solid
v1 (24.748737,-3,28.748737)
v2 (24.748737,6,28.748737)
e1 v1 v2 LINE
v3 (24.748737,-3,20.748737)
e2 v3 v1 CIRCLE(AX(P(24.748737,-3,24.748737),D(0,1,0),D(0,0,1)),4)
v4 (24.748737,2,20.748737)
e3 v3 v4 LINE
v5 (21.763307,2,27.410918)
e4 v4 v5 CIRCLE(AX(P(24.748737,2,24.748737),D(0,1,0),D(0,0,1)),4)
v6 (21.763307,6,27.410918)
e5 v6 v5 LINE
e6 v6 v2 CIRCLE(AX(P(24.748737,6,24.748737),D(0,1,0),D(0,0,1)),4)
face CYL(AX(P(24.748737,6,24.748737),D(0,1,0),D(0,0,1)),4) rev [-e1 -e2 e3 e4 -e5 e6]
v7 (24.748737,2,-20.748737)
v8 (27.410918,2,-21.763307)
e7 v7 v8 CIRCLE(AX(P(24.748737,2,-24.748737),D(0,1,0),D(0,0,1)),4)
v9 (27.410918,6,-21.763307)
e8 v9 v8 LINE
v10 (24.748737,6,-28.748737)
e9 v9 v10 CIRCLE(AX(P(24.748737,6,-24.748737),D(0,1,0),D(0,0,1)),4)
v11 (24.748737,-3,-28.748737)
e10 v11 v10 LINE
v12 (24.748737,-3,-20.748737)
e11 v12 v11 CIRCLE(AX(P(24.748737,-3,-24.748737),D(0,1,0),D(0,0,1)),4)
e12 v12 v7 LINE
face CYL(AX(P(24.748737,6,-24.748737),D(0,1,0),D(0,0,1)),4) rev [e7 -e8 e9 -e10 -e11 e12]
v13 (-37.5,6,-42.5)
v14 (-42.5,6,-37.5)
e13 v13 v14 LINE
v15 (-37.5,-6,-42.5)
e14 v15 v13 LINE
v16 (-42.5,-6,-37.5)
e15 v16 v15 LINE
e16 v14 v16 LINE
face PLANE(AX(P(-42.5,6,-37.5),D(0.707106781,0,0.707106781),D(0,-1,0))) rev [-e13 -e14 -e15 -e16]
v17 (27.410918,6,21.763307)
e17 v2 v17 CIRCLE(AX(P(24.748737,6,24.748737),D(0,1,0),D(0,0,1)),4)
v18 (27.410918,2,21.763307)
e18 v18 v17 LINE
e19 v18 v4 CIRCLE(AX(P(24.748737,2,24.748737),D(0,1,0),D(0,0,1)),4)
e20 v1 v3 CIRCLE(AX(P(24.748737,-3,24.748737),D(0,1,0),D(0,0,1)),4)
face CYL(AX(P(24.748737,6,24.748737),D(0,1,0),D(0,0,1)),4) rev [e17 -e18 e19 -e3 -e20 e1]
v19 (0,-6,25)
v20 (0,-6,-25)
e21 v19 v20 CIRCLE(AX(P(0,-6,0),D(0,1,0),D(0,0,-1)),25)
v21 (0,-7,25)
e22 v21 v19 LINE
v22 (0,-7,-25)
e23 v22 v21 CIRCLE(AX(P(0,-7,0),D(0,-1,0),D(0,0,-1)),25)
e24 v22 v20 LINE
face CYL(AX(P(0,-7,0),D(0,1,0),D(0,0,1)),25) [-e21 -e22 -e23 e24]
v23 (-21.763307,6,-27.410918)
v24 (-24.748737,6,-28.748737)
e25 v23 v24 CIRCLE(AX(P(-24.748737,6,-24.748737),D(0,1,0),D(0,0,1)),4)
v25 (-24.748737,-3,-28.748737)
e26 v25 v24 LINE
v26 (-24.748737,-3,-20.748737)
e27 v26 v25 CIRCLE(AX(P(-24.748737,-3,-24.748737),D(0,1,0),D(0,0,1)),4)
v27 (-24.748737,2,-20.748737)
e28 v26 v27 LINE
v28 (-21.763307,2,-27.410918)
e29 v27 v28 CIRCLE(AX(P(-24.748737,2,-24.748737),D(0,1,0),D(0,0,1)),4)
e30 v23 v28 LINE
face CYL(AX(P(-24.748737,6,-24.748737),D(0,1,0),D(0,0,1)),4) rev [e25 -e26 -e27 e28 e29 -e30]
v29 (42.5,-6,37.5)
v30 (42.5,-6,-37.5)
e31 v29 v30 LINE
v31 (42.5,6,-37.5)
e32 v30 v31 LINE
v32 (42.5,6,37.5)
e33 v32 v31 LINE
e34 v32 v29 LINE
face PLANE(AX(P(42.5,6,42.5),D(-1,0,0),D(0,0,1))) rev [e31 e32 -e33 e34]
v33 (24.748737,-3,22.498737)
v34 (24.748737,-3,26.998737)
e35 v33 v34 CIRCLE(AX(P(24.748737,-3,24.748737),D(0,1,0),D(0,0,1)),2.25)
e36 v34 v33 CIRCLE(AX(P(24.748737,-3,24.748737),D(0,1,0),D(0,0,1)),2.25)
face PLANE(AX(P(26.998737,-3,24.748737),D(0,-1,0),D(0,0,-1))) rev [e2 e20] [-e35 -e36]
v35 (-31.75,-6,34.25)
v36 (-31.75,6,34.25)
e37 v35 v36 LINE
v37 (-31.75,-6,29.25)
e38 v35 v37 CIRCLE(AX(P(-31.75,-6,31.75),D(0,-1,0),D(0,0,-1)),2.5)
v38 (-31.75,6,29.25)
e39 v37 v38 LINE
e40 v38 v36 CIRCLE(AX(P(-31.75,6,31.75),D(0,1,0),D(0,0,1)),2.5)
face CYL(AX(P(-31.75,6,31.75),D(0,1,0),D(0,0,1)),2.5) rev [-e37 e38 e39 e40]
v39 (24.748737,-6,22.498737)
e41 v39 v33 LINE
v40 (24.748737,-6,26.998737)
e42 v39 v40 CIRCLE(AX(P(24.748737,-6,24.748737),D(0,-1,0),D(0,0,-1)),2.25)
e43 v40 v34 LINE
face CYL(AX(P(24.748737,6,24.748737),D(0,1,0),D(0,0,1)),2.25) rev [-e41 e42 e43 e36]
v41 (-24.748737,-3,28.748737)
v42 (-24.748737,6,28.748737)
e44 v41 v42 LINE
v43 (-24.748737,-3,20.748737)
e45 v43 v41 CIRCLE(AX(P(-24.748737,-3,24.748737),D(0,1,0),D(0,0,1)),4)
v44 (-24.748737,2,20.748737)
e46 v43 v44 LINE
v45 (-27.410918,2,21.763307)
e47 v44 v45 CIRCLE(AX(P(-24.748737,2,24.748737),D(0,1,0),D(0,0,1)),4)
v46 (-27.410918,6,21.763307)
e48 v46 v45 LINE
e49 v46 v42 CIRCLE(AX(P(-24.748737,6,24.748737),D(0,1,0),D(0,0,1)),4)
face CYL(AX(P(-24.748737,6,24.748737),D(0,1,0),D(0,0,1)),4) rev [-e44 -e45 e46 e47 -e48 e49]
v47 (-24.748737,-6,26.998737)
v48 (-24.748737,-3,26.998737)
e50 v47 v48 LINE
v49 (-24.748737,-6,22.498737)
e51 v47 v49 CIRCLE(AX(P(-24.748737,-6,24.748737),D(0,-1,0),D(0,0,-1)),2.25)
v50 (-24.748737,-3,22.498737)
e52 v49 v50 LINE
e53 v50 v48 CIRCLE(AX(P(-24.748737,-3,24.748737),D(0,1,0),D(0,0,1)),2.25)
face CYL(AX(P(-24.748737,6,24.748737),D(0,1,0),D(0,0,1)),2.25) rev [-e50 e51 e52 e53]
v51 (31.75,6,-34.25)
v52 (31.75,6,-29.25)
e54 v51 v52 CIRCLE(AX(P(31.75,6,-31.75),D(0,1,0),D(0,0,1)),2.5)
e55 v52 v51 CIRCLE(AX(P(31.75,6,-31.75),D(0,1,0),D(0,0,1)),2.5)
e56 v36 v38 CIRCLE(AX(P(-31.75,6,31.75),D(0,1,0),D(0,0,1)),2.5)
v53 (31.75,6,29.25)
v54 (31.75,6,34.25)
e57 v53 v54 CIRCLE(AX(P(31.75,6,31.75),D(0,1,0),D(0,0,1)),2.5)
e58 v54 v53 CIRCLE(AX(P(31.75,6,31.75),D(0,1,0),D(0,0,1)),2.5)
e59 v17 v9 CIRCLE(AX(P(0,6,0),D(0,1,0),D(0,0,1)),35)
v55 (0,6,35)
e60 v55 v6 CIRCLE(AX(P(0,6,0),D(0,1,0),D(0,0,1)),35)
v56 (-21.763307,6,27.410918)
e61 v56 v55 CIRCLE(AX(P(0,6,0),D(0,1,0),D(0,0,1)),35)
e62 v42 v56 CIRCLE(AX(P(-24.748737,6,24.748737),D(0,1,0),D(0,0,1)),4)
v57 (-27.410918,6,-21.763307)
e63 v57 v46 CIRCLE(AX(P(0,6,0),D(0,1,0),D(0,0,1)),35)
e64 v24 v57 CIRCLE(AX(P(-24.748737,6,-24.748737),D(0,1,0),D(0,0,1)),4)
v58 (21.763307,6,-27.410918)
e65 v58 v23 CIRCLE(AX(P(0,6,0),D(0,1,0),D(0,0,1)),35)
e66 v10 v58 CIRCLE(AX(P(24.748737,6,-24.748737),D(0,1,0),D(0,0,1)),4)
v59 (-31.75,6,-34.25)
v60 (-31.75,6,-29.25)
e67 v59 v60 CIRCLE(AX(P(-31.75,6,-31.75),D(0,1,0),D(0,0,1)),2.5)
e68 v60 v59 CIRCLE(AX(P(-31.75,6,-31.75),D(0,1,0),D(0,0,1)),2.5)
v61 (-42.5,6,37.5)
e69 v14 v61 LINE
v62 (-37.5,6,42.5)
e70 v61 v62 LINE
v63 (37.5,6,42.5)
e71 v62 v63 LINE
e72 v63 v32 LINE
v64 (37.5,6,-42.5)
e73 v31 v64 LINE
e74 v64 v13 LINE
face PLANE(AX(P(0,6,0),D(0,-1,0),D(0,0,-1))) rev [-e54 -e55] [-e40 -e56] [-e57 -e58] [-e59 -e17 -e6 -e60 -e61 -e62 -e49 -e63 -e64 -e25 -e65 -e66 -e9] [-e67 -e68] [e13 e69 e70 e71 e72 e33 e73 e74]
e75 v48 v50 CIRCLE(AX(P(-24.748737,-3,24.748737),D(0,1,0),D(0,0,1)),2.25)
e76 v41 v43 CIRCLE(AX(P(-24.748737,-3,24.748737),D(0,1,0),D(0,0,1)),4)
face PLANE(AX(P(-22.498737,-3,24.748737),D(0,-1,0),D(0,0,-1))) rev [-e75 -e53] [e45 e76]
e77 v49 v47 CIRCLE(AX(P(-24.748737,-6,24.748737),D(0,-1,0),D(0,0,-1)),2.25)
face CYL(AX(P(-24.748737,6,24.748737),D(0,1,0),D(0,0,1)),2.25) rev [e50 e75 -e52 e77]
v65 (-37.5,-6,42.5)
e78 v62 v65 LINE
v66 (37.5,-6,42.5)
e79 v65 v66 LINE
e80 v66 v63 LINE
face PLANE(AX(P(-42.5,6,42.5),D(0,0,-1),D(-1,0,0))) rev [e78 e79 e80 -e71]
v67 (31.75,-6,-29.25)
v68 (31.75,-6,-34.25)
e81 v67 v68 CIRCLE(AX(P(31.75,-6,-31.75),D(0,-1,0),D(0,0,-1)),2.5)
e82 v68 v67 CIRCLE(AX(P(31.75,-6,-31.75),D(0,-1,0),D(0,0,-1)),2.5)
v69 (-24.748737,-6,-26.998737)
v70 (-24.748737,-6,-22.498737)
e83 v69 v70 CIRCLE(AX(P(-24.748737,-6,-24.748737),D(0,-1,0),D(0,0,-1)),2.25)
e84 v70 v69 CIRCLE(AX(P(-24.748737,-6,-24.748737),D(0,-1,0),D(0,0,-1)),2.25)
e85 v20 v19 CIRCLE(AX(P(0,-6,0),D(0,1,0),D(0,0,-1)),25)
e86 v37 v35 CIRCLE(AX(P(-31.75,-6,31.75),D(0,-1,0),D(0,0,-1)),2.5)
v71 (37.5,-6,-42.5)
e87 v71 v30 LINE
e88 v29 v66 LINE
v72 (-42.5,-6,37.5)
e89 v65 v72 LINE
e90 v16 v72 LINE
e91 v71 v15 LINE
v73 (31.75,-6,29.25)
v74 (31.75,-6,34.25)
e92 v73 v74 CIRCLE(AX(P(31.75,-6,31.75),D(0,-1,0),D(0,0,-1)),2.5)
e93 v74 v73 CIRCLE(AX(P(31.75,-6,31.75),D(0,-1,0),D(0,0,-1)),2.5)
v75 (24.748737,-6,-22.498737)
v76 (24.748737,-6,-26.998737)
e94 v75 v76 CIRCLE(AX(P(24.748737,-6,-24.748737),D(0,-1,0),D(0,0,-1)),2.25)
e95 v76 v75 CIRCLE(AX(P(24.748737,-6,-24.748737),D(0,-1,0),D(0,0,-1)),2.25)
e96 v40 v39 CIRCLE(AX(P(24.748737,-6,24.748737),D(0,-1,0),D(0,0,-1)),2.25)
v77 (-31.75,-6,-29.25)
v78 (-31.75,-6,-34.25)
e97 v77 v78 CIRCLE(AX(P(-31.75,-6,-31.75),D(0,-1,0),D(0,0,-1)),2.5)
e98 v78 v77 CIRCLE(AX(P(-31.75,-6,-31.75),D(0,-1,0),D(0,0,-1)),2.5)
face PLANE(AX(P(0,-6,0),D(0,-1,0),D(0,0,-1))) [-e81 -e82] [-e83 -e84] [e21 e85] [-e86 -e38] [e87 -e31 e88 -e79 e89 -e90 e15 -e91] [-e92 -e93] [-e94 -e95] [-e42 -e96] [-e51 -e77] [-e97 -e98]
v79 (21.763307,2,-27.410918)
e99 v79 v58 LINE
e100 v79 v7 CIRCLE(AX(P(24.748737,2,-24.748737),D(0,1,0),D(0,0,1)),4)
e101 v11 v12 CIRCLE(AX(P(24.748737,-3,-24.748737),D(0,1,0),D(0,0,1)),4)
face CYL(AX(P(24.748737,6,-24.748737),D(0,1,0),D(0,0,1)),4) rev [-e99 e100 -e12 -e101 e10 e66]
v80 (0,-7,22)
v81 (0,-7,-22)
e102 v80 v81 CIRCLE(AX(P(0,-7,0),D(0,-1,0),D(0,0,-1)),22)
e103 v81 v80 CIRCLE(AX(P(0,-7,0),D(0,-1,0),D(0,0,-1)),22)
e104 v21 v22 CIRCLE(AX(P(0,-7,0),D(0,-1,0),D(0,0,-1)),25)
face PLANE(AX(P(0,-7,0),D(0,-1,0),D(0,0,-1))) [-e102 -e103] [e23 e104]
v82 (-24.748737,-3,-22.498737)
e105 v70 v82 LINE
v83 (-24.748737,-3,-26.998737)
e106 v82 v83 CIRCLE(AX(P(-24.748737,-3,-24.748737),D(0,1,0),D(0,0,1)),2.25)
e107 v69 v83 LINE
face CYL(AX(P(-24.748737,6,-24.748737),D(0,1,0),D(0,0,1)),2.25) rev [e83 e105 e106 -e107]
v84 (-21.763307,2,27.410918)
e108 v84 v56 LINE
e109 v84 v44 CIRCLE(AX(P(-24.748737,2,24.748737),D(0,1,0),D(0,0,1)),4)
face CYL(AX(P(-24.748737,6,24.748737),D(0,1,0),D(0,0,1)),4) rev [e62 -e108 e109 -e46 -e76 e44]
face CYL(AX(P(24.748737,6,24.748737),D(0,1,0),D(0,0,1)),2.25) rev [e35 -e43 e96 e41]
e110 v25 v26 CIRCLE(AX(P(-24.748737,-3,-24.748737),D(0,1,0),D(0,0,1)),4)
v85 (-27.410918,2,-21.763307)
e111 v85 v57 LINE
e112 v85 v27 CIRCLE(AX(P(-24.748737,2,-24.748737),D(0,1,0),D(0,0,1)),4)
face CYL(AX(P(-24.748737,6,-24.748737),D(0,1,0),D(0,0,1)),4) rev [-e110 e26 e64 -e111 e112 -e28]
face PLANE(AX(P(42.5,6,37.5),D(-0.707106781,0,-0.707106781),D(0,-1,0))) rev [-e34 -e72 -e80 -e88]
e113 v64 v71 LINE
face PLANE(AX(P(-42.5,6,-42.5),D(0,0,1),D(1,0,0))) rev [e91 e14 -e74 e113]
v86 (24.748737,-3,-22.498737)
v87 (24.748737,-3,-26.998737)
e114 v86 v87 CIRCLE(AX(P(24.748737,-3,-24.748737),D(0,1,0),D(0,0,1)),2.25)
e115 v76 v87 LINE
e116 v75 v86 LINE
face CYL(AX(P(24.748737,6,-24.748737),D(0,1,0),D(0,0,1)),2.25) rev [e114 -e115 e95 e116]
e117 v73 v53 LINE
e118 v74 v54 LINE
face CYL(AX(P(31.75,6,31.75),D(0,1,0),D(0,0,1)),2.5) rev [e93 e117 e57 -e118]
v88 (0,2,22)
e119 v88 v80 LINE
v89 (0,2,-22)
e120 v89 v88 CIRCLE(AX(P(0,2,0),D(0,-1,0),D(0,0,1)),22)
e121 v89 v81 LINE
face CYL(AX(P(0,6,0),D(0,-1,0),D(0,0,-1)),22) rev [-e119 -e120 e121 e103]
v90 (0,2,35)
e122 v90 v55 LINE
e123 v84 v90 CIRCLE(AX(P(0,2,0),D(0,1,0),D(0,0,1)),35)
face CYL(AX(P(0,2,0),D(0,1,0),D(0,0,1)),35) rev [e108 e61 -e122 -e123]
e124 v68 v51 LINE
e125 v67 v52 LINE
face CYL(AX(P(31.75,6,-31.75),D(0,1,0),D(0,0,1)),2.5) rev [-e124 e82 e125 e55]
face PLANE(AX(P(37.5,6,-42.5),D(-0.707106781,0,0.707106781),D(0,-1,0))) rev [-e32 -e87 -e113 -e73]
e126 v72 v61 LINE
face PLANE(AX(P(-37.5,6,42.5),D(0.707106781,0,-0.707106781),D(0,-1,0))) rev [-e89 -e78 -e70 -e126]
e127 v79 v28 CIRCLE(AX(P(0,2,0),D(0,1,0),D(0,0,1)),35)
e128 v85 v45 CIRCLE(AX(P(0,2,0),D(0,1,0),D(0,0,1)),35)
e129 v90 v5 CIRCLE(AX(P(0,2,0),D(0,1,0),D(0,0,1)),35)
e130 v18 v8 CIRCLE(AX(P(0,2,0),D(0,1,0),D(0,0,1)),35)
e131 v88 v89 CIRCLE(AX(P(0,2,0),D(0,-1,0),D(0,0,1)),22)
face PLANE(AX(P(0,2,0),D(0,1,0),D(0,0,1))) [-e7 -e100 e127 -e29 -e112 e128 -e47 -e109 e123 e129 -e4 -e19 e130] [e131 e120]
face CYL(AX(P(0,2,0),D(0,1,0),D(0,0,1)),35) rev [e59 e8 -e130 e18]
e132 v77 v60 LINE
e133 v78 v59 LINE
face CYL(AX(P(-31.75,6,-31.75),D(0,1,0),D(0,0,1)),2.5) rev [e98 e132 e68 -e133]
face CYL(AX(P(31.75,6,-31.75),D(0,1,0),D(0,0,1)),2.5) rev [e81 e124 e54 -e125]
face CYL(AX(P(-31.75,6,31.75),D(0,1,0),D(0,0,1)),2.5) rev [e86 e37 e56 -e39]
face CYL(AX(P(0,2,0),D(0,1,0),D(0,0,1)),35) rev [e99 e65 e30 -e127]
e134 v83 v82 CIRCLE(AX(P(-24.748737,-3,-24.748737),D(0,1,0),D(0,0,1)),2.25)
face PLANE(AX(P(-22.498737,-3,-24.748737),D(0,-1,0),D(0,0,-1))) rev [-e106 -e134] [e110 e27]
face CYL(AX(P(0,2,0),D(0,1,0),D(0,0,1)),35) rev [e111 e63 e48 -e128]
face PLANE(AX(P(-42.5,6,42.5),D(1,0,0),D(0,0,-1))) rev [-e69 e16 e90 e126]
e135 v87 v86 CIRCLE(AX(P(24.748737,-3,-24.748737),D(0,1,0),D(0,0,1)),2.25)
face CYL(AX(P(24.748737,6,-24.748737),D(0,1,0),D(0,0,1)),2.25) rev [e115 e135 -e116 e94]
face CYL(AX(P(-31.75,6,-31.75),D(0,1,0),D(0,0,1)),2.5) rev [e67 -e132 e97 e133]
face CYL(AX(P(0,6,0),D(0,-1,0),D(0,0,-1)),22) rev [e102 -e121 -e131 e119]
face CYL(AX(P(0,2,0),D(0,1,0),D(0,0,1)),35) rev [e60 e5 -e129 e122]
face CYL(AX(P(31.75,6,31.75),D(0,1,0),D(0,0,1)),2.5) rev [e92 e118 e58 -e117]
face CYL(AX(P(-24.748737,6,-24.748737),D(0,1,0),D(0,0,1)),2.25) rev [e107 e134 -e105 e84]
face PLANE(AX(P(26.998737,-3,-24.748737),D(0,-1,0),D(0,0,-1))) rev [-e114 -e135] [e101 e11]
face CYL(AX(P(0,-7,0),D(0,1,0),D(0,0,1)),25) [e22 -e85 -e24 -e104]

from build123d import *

# Parameters (mm, degrees)
SKETCH_1_W             = 85
SKETCH_1_H             = 85
EXTRUDE_1_DEPTH        = 6
SKETCH_2_R             = 25
EXTRUDE_2_DEPTH        = 1
SKETCH_3_R             = 22
CUT_EXTRUDE_1_DEPTH    = 62.493902137
SKETCH_4_R             = 35
CUT_EXTRUDE_2_DEPTH    = 4
HOLE_WIZARD_M6_1_D     = 5
CHAMFER_1_SIZE         = 5
PZ_000000C_D           = 4.5
PZ_000000C_CBORE_D     = 8
PZ_000000C_CBORE_DEPTH = 9


with BuildPart() as part:
    # 草图1 → 凸台-拉伸1 (new, symmetric)
    with BuildSketch(Plane(origin=(0, 0, 0), x_dir=(1, 0, 0), z_dir=(0, 1, 0))):
        Rectangle(SKETCH_1_W, SKETCH_1_H)
    extrude(amount=EXTRUDE_1_DEPTH, both=True)

    # 草图2 → 凸台-拉伸2 (add, symmetric)
    with BuildSketch(Plane.XZ.offset(6)):
        with Locations(Location((0, 0, 0), (0, 0, 270))):
            Circle(SKETCH_2_R)
    extrude(amount=EXTRUDE_2_DEPTH, both=True)

    # 草图3 → 切除-拉伸1 (cut, through all)
    with BuildSketch(Plane.XZ.offset(7)):
        with Locations(Location((0, 0, 0), (0, 0, 270))):
            Circle(SKETCH_3_R)
    extrude(amount=-CUT_EXTRUDE_1_DEPTH, mode=Mode.SUBTRACT)

    # 草图4 → 切除-拉伸2 (cut)
    with BuildSketch(Plane(origin=(0, 6, 0), x_dir=(1, 0, 0), z_dir=(0, 1, 0))):
        with Locations(Location((0, 0, 0), (0, 0, 270))):
            Circle(SKETCH_4_R)
    extrude(amount=-CUT_EXTRUDE_2_DEPTH, mode=Mode.SUBTRACT)

    # M6 螺纹孔1 (through all)
    with Locations(Plane(origin=(0, 6, 0), x_dir=(1, 0, 0), z_dir=(0, 1, 0))):
        with Locations((-31.75, 31.75), (0, 0), (31.75, -31.75), (31.75, 31.75), (-31.75, -31.75)):
            Hole(HOLE_WIZARD_M6_1_D / 2)

    # 倒角1
    chamfer_1_edges = [part.edges().sort_by_distance(p)[0] for p in [
        (42.5, 0, 42.5),
        (-42.5, 0, 42.5),
        (-42.5, 0, -42.5),
        (42.5, 0, -42.5),
    ]]
    chamfer(chamfer_1_edges, length=CHAMFER_1_SIZE)

    # PZ-000000C 铺砖车 (through all)
    with Locations(Plane(origin=(0, 6, 0), x_dir=(1, 0, 0), z_dir=(0, 1, 0))):
        with Locations((-24.748737342, 24.748737341), (24.748737342, 24.748737342), (24.748737342, -24.748737342), (-24.748737342, -24.748737342)):
            CounterBoreHole(PZ_000000C_D / 2, PZ_000000C_CBORE_D / 2, PZ_000000C_CBORE_DEPTH)


solid = part.part
